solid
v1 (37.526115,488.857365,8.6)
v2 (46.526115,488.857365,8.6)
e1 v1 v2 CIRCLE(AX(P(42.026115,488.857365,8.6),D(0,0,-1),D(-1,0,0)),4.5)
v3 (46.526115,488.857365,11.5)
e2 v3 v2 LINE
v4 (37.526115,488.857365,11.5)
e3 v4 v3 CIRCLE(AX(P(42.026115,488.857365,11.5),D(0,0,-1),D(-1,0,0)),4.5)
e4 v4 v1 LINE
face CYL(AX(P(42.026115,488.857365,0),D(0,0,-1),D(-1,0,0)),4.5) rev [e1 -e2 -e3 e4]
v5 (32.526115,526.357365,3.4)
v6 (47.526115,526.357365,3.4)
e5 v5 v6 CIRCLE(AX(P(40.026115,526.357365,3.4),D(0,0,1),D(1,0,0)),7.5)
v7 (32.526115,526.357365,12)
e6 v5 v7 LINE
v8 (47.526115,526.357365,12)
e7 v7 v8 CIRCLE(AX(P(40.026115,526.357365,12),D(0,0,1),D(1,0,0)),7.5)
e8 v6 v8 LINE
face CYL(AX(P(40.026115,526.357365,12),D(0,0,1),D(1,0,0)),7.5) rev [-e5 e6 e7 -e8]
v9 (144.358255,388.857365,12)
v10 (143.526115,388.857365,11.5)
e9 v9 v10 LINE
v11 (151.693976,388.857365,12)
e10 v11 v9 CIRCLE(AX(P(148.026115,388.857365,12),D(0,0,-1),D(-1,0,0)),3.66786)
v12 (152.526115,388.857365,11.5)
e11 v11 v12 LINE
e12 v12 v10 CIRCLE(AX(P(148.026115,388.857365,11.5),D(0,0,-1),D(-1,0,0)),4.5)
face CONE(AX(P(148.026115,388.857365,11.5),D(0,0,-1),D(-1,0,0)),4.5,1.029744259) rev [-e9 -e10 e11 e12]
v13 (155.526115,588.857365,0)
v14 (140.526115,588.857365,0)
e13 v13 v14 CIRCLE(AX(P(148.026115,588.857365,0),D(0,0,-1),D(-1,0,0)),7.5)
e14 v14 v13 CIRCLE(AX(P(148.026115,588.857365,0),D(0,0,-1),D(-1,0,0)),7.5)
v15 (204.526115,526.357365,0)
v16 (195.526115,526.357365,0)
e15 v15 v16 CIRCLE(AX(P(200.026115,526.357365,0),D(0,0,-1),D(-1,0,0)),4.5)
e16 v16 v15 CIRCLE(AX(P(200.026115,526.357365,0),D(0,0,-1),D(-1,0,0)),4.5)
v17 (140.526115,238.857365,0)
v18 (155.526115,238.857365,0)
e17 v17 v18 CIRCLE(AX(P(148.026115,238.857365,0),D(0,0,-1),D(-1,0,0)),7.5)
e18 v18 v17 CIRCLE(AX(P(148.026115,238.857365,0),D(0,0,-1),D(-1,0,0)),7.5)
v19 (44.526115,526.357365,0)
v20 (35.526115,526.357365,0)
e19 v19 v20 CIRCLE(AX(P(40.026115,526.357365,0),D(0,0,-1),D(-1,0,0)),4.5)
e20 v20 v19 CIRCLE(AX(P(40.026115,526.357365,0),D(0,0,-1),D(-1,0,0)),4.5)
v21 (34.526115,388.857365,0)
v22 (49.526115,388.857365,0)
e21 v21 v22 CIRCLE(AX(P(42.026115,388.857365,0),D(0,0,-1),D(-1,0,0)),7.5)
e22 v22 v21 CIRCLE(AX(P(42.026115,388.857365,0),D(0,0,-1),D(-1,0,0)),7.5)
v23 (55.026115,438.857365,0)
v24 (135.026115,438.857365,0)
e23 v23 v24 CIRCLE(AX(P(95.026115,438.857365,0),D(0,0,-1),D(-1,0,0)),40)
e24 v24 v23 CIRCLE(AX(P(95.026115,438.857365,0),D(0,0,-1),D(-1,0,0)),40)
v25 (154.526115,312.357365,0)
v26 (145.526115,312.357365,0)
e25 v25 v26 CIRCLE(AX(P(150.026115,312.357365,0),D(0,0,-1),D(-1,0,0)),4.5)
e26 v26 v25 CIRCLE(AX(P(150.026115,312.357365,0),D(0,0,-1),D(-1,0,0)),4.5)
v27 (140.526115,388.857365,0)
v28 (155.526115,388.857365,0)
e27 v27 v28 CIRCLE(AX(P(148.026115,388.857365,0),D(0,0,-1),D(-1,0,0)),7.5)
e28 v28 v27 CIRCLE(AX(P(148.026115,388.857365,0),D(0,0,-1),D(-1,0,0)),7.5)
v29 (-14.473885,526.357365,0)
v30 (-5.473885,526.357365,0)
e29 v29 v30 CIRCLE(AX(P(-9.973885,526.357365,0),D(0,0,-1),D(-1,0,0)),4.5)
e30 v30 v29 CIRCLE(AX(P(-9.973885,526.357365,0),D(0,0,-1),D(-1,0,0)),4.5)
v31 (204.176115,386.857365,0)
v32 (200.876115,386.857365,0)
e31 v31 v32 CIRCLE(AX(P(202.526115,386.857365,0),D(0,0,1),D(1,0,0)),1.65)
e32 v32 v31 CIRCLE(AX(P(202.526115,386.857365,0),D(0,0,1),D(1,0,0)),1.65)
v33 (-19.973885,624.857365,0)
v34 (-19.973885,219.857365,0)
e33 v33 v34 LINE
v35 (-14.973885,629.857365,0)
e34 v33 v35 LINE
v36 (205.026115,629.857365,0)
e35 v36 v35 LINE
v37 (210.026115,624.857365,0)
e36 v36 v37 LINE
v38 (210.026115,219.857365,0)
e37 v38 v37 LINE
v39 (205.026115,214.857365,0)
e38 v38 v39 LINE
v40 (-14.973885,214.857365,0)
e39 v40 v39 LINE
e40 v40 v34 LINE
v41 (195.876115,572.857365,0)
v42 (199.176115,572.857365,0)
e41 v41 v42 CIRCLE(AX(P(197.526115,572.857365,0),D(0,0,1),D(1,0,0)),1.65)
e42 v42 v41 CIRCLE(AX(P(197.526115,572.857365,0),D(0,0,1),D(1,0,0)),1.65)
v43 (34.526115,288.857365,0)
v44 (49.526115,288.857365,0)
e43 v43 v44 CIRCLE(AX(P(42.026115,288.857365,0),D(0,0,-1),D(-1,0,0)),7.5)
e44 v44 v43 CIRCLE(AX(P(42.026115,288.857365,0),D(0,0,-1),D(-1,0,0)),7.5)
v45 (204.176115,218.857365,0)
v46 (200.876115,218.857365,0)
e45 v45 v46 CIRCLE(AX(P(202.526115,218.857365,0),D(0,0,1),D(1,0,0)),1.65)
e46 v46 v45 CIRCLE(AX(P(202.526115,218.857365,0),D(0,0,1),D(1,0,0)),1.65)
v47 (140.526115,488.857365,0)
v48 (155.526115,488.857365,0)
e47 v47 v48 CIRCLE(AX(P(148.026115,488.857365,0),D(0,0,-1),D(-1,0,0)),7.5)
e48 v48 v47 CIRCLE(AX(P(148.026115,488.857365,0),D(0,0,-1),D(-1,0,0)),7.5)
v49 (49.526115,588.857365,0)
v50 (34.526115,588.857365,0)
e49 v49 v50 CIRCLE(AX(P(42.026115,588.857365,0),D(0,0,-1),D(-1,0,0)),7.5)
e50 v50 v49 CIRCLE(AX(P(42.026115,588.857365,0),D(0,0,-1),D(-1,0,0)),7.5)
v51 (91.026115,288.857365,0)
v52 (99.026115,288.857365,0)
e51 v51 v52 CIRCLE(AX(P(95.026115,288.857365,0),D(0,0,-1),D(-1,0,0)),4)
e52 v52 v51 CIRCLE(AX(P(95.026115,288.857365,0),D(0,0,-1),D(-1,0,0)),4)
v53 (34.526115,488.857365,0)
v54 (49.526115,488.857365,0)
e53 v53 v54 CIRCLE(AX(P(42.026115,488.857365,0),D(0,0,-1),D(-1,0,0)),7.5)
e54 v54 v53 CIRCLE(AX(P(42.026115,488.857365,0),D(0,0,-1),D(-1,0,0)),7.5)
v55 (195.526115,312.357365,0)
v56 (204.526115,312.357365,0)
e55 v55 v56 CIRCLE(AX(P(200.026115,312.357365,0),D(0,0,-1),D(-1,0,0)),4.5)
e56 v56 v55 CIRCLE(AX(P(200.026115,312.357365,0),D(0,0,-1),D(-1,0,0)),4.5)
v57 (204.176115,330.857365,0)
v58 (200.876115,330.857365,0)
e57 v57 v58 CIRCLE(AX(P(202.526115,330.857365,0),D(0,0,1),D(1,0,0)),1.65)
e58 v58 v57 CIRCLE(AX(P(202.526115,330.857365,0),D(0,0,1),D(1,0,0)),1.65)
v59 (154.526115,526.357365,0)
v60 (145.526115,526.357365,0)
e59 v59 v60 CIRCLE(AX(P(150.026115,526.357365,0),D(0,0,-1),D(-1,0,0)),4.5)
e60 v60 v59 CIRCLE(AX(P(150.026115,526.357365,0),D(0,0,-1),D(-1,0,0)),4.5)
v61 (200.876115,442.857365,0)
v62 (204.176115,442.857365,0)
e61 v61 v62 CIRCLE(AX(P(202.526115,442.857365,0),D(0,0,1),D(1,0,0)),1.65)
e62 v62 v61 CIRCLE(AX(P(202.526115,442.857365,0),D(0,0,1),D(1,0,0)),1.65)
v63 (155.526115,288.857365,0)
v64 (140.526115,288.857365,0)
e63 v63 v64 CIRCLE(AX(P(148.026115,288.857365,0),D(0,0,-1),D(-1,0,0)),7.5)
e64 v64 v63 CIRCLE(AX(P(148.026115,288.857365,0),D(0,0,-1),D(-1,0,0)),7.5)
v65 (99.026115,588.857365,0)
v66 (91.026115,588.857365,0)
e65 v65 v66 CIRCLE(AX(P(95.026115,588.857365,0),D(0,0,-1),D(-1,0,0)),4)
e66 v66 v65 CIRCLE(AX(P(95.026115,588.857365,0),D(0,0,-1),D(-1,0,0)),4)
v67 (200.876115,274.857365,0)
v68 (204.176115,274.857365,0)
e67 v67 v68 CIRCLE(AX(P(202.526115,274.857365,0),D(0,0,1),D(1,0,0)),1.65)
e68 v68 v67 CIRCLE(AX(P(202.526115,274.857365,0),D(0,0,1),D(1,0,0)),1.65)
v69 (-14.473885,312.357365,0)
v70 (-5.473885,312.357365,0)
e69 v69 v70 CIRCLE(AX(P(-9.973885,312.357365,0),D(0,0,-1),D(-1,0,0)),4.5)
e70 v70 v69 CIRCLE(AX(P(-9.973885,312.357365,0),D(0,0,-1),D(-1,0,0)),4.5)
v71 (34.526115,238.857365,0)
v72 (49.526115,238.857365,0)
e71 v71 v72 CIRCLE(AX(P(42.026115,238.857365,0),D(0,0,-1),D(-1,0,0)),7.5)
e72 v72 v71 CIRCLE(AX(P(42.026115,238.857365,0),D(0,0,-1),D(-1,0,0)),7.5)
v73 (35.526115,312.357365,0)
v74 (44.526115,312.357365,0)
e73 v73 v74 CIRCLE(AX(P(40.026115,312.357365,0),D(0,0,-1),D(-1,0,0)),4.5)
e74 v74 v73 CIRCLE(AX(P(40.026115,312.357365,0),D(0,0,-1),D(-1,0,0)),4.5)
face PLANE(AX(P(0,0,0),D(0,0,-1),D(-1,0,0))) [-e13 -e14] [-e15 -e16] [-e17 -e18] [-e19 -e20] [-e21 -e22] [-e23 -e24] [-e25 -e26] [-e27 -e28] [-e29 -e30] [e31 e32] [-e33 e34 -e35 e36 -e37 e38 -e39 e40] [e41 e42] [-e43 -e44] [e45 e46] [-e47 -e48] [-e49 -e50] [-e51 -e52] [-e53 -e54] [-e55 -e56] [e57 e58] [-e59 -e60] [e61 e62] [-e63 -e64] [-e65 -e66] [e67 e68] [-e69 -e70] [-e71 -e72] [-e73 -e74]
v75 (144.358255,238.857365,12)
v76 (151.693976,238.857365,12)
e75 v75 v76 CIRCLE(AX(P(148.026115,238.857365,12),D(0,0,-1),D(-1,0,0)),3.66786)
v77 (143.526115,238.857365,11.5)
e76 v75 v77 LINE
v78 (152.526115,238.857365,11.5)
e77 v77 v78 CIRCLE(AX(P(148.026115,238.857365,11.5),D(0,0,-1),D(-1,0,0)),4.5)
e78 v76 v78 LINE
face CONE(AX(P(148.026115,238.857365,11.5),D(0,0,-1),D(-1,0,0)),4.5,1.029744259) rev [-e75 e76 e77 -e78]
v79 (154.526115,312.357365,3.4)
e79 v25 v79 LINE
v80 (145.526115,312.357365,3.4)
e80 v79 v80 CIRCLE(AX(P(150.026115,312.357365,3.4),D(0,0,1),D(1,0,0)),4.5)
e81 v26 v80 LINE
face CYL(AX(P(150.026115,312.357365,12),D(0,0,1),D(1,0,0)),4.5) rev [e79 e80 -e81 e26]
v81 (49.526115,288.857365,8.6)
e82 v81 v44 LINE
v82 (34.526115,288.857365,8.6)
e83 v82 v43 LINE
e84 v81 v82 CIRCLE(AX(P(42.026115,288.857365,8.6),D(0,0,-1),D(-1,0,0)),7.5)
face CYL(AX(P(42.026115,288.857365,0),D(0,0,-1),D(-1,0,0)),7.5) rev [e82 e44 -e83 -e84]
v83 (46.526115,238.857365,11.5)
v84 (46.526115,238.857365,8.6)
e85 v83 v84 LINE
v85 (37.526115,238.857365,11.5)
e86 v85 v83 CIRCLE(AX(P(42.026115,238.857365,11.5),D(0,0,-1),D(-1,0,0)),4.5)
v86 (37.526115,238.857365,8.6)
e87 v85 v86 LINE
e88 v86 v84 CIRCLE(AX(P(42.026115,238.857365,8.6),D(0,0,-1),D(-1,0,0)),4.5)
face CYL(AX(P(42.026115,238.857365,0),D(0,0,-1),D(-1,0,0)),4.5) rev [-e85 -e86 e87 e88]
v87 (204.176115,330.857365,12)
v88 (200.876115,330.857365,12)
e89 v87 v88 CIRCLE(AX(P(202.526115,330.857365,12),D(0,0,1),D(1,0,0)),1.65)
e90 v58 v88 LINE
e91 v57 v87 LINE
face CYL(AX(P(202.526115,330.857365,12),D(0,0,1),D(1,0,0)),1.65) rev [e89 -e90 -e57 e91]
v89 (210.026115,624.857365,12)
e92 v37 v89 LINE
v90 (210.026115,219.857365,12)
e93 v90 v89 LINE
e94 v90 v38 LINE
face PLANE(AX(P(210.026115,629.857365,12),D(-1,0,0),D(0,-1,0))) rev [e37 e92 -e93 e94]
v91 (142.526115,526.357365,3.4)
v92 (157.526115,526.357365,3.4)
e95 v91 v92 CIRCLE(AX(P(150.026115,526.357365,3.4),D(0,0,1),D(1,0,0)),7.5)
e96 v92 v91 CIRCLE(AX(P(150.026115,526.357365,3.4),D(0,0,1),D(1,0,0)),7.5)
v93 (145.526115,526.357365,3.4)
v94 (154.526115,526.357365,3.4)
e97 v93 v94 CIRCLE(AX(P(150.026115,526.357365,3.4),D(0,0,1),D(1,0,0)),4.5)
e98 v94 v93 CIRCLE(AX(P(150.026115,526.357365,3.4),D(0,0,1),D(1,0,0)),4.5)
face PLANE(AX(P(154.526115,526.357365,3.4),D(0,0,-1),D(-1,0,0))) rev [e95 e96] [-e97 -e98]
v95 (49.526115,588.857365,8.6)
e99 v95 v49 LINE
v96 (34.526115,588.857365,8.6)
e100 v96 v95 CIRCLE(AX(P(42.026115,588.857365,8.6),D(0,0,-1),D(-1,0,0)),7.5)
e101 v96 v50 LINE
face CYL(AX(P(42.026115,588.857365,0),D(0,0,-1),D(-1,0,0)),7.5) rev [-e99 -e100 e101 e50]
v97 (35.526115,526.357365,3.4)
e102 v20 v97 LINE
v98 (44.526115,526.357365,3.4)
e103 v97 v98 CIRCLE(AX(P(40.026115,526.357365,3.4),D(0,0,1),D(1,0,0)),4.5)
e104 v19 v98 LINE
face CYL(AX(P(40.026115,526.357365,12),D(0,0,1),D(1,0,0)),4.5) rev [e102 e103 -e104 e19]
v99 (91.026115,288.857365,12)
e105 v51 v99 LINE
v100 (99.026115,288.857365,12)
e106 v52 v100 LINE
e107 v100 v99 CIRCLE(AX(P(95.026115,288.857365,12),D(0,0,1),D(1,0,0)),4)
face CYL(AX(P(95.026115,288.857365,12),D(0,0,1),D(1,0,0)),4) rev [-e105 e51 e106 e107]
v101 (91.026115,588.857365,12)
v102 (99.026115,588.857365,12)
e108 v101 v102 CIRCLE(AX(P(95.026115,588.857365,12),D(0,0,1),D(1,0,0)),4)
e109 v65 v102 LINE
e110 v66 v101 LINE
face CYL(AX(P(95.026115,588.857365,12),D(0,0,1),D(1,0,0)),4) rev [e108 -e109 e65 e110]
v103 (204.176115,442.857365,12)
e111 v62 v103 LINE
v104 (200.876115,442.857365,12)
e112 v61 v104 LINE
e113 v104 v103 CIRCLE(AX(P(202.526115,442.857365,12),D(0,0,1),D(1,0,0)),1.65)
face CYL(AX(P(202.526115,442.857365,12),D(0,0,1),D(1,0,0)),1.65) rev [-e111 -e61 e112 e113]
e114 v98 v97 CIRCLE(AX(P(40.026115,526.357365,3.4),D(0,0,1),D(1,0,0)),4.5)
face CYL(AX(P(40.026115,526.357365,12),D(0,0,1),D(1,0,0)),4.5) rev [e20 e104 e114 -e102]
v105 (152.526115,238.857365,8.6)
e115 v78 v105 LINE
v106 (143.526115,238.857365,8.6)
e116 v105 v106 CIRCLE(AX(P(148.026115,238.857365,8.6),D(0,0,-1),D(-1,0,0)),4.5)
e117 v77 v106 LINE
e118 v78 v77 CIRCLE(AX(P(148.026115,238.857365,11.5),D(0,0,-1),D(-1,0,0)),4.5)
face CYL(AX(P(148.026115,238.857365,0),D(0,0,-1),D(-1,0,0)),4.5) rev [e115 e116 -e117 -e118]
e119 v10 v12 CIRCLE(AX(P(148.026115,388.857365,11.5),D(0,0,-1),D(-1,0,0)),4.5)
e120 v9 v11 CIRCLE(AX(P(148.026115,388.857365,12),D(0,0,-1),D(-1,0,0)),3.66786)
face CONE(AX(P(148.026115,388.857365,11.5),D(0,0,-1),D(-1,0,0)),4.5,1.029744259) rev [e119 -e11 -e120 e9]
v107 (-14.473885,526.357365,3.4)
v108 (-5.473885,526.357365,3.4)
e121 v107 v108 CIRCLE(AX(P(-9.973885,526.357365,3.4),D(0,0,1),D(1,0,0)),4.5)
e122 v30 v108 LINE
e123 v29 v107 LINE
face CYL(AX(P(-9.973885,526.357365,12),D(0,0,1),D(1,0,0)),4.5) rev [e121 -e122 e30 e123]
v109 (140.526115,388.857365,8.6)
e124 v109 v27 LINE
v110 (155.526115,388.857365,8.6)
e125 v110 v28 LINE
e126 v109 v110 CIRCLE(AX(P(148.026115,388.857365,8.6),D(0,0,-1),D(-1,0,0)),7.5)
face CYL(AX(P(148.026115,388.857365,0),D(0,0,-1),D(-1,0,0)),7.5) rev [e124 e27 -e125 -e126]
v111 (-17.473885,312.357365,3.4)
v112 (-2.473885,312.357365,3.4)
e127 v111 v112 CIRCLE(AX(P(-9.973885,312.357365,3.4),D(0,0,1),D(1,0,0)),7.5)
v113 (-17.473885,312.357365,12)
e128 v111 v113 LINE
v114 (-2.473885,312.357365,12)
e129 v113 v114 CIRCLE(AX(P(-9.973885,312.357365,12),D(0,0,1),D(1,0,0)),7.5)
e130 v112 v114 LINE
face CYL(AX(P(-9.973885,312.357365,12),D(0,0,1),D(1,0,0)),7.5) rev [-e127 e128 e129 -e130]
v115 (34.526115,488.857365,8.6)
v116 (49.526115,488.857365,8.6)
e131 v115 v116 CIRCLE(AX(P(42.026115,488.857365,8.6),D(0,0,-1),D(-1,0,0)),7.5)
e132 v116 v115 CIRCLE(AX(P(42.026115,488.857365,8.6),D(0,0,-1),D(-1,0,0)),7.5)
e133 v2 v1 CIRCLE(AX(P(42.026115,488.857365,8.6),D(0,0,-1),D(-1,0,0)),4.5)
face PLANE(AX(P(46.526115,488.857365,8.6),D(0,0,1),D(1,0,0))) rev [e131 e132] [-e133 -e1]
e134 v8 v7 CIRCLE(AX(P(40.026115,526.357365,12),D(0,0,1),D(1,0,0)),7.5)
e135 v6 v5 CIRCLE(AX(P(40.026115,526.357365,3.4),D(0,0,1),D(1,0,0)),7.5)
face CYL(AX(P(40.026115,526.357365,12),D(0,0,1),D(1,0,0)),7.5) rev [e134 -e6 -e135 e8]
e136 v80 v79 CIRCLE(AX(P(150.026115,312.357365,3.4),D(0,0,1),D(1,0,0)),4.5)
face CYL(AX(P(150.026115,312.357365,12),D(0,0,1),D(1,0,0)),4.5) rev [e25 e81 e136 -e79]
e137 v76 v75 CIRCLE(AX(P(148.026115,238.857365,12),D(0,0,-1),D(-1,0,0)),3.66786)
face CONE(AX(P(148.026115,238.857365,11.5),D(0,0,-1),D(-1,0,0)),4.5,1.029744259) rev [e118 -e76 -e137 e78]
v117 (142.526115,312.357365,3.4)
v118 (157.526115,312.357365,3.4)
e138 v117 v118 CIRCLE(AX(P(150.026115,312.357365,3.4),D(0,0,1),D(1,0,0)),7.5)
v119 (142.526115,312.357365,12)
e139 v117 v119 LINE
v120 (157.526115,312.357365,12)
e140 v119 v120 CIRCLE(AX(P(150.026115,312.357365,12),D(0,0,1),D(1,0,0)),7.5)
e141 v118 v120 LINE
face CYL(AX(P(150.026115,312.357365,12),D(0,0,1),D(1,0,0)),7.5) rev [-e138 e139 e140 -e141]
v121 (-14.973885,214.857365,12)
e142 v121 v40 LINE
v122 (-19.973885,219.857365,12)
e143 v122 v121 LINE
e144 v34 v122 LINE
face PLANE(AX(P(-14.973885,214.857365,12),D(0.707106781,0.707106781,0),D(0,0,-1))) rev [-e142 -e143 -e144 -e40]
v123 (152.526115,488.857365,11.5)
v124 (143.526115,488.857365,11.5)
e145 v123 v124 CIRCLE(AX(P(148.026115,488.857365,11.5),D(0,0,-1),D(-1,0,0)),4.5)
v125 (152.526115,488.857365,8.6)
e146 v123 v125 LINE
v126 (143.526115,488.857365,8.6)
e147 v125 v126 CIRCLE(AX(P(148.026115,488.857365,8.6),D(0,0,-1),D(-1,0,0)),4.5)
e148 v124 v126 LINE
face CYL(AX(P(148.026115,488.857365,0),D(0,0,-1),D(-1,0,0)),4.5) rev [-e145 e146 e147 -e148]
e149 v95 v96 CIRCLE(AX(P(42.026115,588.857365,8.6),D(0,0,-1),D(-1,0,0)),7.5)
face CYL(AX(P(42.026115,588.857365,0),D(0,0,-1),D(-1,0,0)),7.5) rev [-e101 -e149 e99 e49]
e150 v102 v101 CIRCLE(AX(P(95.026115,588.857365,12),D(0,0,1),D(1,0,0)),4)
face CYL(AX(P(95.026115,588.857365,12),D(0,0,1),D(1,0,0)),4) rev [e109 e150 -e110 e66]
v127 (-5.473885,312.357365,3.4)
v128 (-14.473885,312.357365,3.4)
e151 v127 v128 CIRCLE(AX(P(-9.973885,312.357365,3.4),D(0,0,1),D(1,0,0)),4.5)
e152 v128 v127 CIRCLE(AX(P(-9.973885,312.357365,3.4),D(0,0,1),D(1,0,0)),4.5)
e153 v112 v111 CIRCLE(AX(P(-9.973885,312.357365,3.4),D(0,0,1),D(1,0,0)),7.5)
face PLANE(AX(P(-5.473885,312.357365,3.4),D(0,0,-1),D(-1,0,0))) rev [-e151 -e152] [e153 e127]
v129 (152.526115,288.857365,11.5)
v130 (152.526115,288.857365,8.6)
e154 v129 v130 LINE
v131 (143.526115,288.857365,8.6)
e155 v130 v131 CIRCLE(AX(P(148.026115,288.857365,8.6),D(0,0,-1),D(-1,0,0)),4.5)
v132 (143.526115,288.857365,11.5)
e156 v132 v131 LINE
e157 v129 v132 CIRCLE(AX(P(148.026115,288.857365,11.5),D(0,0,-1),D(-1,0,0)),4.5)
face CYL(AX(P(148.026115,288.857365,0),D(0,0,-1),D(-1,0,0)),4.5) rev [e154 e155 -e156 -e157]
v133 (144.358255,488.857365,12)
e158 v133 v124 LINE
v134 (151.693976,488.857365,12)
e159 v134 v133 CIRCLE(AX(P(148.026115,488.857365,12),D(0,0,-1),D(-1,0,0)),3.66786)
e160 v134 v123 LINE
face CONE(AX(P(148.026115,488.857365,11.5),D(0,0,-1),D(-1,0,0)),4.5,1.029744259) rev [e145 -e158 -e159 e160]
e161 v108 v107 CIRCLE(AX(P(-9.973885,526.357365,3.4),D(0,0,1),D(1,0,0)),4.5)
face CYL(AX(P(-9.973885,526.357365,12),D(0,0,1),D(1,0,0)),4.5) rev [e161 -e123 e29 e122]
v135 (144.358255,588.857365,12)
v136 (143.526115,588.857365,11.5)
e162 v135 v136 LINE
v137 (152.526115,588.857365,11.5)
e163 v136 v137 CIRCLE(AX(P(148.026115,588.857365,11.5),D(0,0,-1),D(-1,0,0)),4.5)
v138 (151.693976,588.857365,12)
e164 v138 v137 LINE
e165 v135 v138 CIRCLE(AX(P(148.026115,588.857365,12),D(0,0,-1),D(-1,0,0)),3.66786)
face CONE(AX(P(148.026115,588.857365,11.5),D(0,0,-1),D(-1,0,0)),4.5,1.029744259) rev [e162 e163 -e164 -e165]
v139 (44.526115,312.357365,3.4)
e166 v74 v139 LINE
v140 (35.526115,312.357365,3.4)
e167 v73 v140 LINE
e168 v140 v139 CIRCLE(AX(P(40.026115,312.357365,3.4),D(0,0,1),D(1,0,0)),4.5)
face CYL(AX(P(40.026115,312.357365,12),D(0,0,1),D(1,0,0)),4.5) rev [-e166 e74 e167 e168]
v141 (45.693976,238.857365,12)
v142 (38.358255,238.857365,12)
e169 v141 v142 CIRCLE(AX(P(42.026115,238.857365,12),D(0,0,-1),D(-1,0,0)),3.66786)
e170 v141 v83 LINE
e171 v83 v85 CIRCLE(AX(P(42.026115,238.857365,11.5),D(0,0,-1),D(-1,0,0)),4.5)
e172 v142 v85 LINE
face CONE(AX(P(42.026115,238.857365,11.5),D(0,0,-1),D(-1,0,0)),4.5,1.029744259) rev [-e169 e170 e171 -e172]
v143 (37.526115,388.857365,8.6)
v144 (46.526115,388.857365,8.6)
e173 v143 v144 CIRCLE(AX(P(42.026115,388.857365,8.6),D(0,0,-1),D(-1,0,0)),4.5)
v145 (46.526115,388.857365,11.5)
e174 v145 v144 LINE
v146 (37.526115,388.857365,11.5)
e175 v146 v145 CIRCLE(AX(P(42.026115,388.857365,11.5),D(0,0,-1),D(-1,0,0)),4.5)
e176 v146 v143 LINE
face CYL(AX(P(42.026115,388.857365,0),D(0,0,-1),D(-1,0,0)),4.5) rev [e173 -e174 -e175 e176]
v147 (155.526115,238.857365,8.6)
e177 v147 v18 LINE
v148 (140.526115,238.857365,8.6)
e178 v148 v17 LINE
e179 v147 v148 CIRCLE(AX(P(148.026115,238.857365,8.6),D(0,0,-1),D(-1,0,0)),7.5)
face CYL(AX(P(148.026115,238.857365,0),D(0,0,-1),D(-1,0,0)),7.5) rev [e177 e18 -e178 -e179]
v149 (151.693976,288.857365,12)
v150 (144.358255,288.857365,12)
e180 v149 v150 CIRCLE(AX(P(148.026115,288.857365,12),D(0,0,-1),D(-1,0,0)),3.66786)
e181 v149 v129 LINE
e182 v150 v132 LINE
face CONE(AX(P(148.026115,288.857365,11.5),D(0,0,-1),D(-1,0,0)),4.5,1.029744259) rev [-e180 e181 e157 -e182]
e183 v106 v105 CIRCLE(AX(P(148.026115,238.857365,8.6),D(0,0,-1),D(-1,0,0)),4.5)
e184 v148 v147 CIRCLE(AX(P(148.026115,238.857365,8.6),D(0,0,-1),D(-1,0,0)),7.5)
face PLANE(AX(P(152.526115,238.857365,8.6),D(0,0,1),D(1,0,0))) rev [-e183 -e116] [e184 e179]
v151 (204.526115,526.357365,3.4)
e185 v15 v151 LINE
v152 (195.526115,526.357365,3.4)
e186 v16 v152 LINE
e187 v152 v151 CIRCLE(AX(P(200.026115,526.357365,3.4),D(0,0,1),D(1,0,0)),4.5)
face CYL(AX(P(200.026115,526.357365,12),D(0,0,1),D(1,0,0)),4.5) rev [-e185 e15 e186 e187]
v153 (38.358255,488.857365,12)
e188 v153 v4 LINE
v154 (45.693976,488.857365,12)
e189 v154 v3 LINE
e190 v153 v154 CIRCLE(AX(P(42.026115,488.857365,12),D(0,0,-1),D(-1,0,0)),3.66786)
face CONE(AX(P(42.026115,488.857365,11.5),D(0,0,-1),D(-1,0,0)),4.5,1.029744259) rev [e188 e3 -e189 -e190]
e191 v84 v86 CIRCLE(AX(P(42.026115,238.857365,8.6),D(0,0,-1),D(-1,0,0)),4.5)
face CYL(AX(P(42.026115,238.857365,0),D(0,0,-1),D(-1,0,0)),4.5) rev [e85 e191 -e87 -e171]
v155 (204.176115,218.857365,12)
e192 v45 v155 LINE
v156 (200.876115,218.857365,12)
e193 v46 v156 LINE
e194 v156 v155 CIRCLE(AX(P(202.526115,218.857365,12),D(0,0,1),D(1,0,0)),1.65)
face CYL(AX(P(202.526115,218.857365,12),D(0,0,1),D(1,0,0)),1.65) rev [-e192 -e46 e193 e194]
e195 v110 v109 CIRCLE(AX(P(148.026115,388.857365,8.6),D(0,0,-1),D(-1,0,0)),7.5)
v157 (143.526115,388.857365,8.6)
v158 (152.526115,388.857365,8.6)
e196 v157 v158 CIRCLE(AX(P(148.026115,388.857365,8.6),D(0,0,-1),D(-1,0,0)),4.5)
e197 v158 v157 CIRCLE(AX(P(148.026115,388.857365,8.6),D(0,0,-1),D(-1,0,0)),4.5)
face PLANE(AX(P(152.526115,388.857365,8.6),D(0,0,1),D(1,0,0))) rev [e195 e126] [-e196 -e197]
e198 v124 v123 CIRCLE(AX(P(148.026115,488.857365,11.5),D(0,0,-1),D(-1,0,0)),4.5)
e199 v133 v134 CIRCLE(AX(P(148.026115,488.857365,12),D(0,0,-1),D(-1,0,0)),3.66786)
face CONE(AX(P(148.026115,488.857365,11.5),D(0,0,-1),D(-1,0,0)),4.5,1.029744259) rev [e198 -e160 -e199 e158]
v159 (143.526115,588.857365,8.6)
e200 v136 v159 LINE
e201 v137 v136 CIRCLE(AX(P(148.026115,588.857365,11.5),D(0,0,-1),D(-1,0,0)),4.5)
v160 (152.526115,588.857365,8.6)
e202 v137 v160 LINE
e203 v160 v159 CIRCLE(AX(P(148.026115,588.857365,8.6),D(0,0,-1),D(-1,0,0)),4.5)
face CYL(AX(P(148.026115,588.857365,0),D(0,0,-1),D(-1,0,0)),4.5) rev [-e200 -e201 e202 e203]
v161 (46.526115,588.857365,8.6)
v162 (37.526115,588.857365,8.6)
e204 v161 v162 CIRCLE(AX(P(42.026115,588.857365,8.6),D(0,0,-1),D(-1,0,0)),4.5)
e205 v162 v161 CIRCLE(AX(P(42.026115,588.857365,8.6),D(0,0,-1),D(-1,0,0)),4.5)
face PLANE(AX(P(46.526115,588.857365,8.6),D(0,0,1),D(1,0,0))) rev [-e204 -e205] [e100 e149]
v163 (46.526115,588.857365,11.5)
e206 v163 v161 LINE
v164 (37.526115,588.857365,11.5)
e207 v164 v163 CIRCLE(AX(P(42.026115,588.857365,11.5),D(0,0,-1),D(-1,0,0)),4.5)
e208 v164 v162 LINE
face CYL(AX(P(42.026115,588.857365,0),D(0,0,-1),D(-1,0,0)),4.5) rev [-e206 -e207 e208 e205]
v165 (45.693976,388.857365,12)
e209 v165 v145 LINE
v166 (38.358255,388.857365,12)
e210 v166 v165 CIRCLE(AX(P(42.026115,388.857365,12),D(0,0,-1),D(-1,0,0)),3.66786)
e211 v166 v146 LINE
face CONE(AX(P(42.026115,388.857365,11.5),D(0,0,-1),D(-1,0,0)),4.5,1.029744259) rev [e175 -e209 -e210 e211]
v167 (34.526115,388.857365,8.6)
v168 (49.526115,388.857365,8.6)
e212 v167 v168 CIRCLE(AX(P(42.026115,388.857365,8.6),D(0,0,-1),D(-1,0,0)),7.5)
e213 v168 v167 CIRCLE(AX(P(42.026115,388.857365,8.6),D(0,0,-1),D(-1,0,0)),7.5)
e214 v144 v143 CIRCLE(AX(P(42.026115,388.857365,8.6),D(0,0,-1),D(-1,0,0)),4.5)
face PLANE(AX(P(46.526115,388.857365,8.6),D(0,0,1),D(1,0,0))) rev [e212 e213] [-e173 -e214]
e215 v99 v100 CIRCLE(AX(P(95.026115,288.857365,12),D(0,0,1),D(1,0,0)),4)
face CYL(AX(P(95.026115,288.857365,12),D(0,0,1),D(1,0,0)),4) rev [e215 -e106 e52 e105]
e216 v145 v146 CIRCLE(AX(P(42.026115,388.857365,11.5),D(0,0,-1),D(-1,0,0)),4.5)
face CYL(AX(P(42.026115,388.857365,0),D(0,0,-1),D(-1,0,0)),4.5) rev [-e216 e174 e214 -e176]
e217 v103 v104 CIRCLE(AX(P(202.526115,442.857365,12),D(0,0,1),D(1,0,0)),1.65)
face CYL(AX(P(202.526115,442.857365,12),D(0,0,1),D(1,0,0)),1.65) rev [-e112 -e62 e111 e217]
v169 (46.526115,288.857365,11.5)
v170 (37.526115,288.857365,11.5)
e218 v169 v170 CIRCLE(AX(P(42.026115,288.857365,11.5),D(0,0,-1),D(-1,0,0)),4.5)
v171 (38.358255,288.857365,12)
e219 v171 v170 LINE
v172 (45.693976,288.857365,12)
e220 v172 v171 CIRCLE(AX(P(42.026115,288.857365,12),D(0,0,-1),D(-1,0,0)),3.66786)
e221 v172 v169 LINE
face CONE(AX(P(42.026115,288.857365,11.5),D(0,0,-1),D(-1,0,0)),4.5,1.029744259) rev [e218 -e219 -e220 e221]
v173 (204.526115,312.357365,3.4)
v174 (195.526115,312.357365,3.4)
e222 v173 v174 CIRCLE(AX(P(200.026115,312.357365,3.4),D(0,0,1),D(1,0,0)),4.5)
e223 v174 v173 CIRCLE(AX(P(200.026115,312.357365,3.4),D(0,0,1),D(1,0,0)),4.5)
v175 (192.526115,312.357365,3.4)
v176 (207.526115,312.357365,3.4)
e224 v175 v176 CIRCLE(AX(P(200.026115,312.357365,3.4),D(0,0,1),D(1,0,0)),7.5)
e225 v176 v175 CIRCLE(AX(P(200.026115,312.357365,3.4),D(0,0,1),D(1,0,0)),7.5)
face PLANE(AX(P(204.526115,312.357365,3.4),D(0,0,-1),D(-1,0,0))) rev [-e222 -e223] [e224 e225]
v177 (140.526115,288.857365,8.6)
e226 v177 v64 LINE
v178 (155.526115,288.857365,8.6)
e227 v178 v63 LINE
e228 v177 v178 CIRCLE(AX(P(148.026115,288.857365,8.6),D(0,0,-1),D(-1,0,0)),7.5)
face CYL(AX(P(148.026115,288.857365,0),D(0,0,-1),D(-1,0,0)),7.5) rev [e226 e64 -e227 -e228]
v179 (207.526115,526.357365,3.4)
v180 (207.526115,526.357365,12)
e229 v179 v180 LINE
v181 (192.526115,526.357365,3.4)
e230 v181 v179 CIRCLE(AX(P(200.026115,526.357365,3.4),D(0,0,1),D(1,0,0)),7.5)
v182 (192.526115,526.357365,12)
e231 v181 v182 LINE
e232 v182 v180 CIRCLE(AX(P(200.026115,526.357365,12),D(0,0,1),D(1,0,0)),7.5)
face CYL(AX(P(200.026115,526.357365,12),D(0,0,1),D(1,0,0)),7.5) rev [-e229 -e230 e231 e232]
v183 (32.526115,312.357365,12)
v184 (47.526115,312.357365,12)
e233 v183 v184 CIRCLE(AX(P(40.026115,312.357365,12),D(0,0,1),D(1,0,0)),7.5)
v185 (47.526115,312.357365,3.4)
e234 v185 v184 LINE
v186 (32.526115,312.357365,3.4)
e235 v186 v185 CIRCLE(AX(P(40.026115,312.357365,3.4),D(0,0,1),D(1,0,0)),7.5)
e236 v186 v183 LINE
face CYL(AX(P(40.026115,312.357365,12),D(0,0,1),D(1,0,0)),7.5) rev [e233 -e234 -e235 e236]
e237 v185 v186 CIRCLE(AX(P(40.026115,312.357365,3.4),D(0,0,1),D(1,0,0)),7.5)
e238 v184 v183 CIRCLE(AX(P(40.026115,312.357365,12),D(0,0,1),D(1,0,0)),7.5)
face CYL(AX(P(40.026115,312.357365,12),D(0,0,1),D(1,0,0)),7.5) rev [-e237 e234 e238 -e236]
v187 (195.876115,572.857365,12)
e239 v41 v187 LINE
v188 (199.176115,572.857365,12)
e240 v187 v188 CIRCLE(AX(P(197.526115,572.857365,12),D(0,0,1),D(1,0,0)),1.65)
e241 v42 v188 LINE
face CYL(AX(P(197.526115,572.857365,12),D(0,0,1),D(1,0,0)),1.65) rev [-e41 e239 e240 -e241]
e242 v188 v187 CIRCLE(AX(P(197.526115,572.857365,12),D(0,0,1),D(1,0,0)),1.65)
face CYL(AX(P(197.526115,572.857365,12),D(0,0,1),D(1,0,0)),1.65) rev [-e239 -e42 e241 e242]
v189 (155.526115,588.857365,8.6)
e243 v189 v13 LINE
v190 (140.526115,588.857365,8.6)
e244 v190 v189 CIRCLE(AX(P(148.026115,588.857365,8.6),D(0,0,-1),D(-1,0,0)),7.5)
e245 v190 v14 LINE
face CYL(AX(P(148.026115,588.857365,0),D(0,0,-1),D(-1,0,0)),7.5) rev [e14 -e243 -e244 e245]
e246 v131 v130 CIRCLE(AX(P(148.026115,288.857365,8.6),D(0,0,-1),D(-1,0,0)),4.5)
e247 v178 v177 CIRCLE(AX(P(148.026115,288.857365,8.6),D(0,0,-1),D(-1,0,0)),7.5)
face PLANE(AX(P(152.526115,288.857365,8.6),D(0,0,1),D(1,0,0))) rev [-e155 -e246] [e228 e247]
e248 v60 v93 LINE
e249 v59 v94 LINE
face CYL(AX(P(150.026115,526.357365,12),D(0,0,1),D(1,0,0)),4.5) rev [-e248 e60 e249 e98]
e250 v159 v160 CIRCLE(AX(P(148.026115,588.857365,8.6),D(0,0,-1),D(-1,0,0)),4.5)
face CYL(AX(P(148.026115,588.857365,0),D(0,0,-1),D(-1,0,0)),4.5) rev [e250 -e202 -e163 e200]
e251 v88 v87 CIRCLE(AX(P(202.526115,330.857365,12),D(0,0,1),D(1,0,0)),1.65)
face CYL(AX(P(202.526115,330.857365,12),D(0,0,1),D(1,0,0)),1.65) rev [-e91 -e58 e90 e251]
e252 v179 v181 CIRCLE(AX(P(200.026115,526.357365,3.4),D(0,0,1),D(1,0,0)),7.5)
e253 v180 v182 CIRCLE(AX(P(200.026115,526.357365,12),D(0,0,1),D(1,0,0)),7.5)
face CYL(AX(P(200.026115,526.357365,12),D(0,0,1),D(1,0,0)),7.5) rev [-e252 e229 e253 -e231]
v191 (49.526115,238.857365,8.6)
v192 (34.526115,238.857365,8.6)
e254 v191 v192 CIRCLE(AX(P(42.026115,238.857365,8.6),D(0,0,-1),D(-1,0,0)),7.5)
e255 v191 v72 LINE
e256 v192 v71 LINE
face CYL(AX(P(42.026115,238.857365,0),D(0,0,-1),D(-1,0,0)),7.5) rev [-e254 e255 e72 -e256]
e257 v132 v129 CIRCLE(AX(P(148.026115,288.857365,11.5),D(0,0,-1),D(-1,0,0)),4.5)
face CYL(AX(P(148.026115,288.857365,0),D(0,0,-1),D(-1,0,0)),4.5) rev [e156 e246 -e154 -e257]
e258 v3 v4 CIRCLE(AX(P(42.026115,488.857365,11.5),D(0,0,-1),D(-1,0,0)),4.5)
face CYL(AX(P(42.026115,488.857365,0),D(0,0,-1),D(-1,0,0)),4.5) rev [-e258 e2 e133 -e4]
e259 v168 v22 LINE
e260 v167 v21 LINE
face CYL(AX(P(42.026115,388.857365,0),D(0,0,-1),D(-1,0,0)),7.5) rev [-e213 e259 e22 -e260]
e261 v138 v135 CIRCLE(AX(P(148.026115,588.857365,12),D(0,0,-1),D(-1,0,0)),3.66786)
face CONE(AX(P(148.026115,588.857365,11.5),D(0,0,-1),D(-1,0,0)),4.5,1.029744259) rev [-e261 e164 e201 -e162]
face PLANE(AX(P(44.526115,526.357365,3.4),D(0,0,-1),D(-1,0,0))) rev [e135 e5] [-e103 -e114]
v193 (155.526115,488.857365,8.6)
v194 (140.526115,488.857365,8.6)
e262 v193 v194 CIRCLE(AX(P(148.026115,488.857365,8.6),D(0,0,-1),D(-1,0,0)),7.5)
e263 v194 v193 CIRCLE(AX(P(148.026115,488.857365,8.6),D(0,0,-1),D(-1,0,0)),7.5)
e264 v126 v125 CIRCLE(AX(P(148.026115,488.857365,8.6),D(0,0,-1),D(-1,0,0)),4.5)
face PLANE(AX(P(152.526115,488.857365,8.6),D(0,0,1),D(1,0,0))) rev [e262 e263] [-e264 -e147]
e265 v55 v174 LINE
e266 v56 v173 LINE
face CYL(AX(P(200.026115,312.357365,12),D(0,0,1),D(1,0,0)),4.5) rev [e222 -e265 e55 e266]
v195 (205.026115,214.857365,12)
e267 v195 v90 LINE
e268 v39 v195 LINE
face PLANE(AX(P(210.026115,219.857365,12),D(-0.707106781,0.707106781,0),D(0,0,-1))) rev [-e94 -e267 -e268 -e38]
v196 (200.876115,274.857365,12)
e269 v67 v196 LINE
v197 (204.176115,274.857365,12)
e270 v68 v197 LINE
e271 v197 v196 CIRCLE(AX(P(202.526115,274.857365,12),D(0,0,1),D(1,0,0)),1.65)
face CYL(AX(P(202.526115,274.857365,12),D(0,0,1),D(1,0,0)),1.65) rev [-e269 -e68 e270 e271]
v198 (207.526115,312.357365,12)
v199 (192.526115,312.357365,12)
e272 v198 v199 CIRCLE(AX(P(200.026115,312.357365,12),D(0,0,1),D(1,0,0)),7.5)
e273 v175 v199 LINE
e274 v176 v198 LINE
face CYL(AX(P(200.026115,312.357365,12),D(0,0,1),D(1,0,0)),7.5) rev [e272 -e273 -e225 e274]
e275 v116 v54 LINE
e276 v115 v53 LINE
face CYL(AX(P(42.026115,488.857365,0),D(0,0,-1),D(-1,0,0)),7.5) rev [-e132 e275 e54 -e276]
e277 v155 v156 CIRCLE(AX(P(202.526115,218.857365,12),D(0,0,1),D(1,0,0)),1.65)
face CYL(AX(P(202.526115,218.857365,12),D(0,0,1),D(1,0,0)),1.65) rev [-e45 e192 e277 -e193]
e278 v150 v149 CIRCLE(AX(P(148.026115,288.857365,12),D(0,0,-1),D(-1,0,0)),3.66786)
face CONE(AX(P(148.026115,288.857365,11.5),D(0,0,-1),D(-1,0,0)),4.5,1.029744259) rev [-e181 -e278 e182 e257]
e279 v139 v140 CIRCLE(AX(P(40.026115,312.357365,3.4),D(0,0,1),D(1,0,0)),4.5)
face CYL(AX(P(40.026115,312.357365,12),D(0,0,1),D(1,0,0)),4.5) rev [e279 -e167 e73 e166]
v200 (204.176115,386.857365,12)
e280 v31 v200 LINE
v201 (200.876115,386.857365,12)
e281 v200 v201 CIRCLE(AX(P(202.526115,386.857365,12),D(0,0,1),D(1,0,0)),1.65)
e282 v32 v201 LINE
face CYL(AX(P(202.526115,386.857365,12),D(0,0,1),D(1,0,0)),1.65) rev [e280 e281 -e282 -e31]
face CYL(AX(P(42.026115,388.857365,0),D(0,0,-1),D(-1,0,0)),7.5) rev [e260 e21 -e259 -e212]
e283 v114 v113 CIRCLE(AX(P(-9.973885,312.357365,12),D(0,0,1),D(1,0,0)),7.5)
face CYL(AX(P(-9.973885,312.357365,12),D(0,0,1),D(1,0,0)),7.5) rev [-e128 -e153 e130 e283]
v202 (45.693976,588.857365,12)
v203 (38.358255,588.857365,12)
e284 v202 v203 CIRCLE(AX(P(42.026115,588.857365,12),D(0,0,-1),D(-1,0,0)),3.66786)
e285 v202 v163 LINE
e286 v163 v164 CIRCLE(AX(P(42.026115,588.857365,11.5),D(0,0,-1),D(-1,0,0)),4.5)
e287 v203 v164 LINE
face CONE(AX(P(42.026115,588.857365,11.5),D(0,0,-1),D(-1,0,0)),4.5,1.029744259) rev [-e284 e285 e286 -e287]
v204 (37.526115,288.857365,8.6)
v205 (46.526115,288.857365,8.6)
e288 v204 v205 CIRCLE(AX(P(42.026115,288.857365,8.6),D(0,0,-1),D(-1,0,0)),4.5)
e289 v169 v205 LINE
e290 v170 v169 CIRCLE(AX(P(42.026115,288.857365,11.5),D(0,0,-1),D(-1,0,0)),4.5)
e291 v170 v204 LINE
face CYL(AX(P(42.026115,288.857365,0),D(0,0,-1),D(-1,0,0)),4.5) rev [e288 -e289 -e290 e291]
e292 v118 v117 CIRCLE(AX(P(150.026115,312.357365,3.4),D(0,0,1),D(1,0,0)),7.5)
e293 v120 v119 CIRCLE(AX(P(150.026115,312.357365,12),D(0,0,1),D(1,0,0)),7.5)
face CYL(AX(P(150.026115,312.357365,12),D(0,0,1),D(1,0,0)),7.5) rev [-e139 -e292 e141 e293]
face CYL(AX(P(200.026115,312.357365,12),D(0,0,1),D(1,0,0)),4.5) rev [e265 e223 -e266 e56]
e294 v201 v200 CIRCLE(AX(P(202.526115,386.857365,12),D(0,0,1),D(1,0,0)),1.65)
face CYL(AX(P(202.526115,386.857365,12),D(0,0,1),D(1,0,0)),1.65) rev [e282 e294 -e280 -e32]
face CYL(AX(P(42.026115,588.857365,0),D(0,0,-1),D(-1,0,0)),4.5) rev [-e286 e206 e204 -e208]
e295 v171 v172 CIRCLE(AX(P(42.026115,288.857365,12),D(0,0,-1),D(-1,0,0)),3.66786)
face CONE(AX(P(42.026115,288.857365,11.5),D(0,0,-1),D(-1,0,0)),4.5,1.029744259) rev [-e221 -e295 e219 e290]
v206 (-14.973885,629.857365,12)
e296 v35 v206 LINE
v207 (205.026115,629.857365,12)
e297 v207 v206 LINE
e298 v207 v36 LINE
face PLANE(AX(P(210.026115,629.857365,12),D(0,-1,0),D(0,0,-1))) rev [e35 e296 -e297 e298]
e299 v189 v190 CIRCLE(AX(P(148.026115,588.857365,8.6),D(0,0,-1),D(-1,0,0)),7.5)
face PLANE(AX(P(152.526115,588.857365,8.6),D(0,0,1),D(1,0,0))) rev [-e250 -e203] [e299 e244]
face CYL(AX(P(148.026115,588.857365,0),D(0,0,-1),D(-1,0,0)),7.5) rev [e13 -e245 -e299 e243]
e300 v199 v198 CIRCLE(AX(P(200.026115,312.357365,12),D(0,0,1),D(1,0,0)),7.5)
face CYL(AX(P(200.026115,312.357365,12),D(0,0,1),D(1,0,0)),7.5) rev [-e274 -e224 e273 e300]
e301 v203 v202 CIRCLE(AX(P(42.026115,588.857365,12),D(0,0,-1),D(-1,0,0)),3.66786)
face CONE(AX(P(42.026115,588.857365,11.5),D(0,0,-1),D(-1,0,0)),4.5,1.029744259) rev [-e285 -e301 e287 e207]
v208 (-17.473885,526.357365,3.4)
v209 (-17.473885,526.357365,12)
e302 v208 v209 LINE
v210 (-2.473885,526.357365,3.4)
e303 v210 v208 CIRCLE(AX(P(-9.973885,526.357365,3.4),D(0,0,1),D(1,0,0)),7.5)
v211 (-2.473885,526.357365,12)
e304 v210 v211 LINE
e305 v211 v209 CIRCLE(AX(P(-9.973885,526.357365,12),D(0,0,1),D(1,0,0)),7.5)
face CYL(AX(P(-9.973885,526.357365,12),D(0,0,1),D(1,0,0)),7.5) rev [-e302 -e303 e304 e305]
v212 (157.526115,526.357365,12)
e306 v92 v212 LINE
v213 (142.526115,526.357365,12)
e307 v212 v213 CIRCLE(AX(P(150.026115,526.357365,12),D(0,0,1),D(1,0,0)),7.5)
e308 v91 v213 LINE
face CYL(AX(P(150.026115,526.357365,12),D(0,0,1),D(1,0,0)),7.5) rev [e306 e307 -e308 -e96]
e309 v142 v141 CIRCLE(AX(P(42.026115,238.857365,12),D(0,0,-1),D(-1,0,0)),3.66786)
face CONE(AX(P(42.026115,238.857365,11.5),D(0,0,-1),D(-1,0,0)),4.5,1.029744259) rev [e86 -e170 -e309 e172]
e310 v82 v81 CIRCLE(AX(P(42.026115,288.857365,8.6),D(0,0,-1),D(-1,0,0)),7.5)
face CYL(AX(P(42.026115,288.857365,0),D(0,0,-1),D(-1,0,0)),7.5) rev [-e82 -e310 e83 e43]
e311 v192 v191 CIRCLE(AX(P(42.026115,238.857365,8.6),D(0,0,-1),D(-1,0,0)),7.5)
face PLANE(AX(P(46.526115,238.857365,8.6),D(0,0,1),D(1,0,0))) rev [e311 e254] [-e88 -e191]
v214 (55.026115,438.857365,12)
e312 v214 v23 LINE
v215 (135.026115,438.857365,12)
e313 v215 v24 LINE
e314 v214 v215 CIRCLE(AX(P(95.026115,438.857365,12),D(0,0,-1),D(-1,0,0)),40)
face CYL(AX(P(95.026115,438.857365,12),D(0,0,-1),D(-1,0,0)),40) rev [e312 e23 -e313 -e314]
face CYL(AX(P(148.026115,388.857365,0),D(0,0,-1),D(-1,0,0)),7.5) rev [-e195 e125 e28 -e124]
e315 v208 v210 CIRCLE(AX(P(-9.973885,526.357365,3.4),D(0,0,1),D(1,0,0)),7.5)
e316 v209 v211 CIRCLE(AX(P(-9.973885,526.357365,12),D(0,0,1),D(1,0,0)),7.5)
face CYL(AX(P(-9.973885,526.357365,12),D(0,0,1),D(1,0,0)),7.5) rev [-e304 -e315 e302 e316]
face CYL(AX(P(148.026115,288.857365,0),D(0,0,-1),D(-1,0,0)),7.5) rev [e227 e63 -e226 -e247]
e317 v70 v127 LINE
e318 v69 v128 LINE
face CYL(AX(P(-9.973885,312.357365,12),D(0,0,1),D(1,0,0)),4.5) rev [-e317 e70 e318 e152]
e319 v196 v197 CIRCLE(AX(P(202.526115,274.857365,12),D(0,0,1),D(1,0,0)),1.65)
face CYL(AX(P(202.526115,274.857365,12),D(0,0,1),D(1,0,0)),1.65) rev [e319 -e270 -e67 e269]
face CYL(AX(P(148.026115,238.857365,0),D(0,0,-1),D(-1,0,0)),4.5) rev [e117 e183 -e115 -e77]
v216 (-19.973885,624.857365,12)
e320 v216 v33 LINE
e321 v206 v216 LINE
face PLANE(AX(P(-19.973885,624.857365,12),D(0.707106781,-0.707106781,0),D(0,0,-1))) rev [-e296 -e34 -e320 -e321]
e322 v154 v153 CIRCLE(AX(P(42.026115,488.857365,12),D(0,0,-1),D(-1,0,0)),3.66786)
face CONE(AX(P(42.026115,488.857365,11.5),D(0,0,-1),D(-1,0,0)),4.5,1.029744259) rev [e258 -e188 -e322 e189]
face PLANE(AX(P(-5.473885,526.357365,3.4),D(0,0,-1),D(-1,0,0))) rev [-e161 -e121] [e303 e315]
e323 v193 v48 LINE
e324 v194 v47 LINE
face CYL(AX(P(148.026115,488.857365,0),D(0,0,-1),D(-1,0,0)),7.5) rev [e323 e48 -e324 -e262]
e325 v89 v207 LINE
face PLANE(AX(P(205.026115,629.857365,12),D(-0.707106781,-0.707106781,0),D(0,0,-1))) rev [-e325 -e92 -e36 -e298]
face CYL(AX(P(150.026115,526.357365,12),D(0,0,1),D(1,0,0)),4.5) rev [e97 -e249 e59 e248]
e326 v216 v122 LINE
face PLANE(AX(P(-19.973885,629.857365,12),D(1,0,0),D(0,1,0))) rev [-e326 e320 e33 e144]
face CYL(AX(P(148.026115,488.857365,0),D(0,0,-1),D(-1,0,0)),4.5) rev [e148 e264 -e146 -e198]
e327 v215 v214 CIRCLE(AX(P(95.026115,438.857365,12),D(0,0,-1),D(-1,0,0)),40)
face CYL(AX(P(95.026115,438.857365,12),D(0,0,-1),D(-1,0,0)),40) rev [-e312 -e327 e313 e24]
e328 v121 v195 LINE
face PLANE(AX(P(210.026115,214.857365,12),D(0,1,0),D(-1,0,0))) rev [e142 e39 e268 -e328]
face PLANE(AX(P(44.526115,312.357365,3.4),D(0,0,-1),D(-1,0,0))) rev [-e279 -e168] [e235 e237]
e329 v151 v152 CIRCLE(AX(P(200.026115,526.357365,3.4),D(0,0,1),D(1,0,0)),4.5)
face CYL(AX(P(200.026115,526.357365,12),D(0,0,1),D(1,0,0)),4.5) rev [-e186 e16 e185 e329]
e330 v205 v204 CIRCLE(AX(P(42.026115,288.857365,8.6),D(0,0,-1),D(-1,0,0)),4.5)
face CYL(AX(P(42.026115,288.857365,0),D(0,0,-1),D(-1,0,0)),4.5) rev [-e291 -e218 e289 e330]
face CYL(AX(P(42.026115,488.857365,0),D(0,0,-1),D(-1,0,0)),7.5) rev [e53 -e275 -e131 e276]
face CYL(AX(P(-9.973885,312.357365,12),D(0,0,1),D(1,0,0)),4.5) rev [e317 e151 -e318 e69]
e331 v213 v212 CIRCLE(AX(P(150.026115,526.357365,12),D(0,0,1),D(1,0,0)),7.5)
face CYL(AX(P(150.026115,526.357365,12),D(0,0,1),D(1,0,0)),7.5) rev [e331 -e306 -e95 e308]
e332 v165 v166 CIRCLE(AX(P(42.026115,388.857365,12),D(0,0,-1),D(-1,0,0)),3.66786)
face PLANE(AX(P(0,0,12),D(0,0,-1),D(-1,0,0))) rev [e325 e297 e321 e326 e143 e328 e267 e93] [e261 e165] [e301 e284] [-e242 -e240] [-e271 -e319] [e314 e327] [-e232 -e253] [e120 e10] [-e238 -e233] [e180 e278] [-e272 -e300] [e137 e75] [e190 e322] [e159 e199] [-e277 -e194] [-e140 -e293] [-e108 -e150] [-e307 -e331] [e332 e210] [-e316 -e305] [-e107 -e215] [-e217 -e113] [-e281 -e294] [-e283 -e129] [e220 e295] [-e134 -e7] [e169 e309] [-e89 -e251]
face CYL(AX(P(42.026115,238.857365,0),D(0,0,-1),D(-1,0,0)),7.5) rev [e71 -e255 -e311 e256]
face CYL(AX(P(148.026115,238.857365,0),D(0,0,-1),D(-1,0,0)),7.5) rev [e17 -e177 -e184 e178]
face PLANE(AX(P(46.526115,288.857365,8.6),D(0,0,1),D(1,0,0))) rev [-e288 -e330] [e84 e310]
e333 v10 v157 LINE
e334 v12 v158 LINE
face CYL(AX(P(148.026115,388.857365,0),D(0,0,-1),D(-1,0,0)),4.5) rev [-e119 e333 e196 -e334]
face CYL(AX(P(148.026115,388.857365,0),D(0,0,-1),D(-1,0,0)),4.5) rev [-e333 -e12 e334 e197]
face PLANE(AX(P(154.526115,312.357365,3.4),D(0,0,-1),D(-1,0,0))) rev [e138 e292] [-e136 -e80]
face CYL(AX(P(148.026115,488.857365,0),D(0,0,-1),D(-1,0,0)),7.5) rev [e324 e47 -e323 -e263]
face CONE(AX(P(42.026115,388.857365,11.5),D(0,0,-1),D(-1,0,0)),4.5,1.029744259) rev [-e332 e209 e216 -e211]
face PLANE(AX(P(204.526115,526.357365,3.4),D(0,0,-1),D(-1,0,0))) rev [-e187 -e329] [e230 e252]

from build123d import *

# Parameters (mm, degrees)
SKETCH_1_W                   = 230
SKETCH_1_H                   = 415
EXTRUDE_1_DEPTH              = 12
CHAMFER_1_SIZE               = 5
HOLE_WIZARD_M8_1_D           = 9
HOLE_WIZARD_M8_1_DEPTH       = 11.5
HOLE_WIZARD_M8_1_CBORE_D     = 15
HOLE_WIZARD_M8_1_CBORE_DEPTH = 8.6
HOLE_WIZARD_M8_1_TIP         = 2.703872786
HOLE_WIZARD_M8_2_D           = 9
HOLE_WIZARD_M8_2_DEPTH       = 22.25
HOLE_WIZARD_M8_2_CBORE_D     = 15
HOLE_WIZARD_M8_2_CBORE_DEPTH = 8.6
HOLE_WIZARD_M8_2_TIP         = 2.703872786
MM_1_D                       = 8
MM_1_DEPTH                   = 22.25
MM_1_TIP                     = 2.403442476
HOLE_WIZARD_M4_1_D           = 3.3
HOLE_WIZARD_M4_2_D           = 3.3
SKETCH_12_R                  = 40
CUT_EXTRUDE_1_DEPTH          = 665.059688056


with BuildPart() as part:
    # 草图1 → 凸台-拉伸1 (new body)
    with BuildSketch(Plane.XY):
        with Locations((95.026115454, 422.357364907)):
            Rectangle(SKETCH_1_W, SKETCH_1_H)
    extrude(amount=EXTRUDE_1_DEPTH)

    # 倒角1
    chamfer_1_edges = [part.edges().sort_by_distance(p)[0] for p in [
        (210.026115454, 214.857364907, 6),
        (-19.973884546, 214.857364907, 6),
        (-19.973884546, 629.857364907, 6),
        (210.026115454, 629.857364907, 6),
    ]]
    chamfer(chamfer_1_edges, length=CHAMFER_1_SIZE)

    # M8 六角凹头螺钉的柱形沉头孔1
    with Locations(Plane(origin=(0, 0, 0), x_dir=(-1, 0, 0), z_dir=(0, 0, -1))):
        with Locations((-148.026115454, 588.857364907), (-42.026115454, 588.857364907), (-148.026115454, 488.857364907), (-42.026115454, 488.857364907), (-148.026115454, 388.857364907), (-42.026115454, 388.857364907), (-148.026115454, 288.857364907), (-42.026115454, 288.857364907), (-148.026115454, 238.857364907), (-42.026115454, 238.857364907)):
            CounterBoreHole(HOLE_WIZARD_M8_1_D / 2, HOLE_WIZARD_M8_1_CBORE_D / 2, HOLE_WIZARD_M8_1_CBORE_DEPTH, depth=HOLE_WIZARD_M8_1_DEPTH)
            with Locations((0, 0, -(HOLE_WIZARD_M8_1_DEPTH + HOLE_WIZARD_M8_1_TIP / 2))):  # 118° drill point
                Cone(0, HOLE_WIZARD_M8_1_D / 2, HOLE_WIZARD_M8_1_TIP, mode=Mode.SUBTRACT)

    # M8 六角凹头螺钉的柱形沉头孔2
    with Locations(Plane.XY.offset(12)):
        with Locations((-9.973884546, 526.357364907), (40.026115454, 526.357364907), (150.026115454, 526.357364907), (200.026115454, 526.357364907), (200.026115454, 312.357364907), (150.026115454, 312.357364907), (40.026115454, 312.357364907), (-9.973884546, 312.357364907)):
            CounterBoreHole(HOLE_WIZARD_M8_2_D / 2, HOLE_WIZARD_M8_2_CBORE_D / 2, HOLE_WIZARD_M8_2_CBORE_DEPTH, depth=HOLE_WIZARD_M8_2_DEPTH)
            with Locations((0, 0, -(HOLE_WIZARD_M8_2_DEPTH + HOLE_WIZARD_M8_2_TIP / 2))):  # 118° drill point
                Cone(0, HOLE_WIZARD_M8_2_D / 2, HOLE_WIZARD_M8_2_TIP, mode=Mode.SUBTRACT)

    # 大小mm 暗销孔1
    with Locations(Plane.XY.offset(12)):
        with Locations((95.026115454, 588.857364907), (95.026115454, 288.857364907)):
            Hole(MM_1_D / 2, depth=MM_1_DEPTH)
            with Locations((0, 0, -(MM_1_DEPTH + MM_1_TIP / 2))):  # 118° drill point
                Cone(0, MM_1_D / 2, MM_1_TIP, mode=Mode.SUBTRACT)

    # M4 螺纹孔1 (through all)
    with Locations(Plane.XY.offset(12)):
        with Locations((202.526115454, 218.857364907), (202.526115454, 274.857364907), (202.526115454, 330.857364907), (202.526115454, 386.857364907), (202.526115454, 442.857364907)):
            Hole(HOLE_WIZARD_M4_1_D / 2)

    # M4 螺纹孔2 (through all)
    with Locations(Plane.XY.offset(12)):
        with Locations((197.526115454, 572.857364907)):
            Hole(HOLE_WIZARD_M4_2_D / 2)

    # 草图12 → 切除-拉伸1 (cut, through all)
    with BuildSketch(Plane(origin=(0, 0, 0), x_dir=(-1, 0, 0), z_dir=(0, 0, -1))):
        with Locations((-95.026115454, 438.857364907)):
            Circle(SKETCH_12_R)
    extrude(amount=-CUT_EXTRUDE_1_DEPTH, mode=Mode.SUBTRACT)


solid = part.part
